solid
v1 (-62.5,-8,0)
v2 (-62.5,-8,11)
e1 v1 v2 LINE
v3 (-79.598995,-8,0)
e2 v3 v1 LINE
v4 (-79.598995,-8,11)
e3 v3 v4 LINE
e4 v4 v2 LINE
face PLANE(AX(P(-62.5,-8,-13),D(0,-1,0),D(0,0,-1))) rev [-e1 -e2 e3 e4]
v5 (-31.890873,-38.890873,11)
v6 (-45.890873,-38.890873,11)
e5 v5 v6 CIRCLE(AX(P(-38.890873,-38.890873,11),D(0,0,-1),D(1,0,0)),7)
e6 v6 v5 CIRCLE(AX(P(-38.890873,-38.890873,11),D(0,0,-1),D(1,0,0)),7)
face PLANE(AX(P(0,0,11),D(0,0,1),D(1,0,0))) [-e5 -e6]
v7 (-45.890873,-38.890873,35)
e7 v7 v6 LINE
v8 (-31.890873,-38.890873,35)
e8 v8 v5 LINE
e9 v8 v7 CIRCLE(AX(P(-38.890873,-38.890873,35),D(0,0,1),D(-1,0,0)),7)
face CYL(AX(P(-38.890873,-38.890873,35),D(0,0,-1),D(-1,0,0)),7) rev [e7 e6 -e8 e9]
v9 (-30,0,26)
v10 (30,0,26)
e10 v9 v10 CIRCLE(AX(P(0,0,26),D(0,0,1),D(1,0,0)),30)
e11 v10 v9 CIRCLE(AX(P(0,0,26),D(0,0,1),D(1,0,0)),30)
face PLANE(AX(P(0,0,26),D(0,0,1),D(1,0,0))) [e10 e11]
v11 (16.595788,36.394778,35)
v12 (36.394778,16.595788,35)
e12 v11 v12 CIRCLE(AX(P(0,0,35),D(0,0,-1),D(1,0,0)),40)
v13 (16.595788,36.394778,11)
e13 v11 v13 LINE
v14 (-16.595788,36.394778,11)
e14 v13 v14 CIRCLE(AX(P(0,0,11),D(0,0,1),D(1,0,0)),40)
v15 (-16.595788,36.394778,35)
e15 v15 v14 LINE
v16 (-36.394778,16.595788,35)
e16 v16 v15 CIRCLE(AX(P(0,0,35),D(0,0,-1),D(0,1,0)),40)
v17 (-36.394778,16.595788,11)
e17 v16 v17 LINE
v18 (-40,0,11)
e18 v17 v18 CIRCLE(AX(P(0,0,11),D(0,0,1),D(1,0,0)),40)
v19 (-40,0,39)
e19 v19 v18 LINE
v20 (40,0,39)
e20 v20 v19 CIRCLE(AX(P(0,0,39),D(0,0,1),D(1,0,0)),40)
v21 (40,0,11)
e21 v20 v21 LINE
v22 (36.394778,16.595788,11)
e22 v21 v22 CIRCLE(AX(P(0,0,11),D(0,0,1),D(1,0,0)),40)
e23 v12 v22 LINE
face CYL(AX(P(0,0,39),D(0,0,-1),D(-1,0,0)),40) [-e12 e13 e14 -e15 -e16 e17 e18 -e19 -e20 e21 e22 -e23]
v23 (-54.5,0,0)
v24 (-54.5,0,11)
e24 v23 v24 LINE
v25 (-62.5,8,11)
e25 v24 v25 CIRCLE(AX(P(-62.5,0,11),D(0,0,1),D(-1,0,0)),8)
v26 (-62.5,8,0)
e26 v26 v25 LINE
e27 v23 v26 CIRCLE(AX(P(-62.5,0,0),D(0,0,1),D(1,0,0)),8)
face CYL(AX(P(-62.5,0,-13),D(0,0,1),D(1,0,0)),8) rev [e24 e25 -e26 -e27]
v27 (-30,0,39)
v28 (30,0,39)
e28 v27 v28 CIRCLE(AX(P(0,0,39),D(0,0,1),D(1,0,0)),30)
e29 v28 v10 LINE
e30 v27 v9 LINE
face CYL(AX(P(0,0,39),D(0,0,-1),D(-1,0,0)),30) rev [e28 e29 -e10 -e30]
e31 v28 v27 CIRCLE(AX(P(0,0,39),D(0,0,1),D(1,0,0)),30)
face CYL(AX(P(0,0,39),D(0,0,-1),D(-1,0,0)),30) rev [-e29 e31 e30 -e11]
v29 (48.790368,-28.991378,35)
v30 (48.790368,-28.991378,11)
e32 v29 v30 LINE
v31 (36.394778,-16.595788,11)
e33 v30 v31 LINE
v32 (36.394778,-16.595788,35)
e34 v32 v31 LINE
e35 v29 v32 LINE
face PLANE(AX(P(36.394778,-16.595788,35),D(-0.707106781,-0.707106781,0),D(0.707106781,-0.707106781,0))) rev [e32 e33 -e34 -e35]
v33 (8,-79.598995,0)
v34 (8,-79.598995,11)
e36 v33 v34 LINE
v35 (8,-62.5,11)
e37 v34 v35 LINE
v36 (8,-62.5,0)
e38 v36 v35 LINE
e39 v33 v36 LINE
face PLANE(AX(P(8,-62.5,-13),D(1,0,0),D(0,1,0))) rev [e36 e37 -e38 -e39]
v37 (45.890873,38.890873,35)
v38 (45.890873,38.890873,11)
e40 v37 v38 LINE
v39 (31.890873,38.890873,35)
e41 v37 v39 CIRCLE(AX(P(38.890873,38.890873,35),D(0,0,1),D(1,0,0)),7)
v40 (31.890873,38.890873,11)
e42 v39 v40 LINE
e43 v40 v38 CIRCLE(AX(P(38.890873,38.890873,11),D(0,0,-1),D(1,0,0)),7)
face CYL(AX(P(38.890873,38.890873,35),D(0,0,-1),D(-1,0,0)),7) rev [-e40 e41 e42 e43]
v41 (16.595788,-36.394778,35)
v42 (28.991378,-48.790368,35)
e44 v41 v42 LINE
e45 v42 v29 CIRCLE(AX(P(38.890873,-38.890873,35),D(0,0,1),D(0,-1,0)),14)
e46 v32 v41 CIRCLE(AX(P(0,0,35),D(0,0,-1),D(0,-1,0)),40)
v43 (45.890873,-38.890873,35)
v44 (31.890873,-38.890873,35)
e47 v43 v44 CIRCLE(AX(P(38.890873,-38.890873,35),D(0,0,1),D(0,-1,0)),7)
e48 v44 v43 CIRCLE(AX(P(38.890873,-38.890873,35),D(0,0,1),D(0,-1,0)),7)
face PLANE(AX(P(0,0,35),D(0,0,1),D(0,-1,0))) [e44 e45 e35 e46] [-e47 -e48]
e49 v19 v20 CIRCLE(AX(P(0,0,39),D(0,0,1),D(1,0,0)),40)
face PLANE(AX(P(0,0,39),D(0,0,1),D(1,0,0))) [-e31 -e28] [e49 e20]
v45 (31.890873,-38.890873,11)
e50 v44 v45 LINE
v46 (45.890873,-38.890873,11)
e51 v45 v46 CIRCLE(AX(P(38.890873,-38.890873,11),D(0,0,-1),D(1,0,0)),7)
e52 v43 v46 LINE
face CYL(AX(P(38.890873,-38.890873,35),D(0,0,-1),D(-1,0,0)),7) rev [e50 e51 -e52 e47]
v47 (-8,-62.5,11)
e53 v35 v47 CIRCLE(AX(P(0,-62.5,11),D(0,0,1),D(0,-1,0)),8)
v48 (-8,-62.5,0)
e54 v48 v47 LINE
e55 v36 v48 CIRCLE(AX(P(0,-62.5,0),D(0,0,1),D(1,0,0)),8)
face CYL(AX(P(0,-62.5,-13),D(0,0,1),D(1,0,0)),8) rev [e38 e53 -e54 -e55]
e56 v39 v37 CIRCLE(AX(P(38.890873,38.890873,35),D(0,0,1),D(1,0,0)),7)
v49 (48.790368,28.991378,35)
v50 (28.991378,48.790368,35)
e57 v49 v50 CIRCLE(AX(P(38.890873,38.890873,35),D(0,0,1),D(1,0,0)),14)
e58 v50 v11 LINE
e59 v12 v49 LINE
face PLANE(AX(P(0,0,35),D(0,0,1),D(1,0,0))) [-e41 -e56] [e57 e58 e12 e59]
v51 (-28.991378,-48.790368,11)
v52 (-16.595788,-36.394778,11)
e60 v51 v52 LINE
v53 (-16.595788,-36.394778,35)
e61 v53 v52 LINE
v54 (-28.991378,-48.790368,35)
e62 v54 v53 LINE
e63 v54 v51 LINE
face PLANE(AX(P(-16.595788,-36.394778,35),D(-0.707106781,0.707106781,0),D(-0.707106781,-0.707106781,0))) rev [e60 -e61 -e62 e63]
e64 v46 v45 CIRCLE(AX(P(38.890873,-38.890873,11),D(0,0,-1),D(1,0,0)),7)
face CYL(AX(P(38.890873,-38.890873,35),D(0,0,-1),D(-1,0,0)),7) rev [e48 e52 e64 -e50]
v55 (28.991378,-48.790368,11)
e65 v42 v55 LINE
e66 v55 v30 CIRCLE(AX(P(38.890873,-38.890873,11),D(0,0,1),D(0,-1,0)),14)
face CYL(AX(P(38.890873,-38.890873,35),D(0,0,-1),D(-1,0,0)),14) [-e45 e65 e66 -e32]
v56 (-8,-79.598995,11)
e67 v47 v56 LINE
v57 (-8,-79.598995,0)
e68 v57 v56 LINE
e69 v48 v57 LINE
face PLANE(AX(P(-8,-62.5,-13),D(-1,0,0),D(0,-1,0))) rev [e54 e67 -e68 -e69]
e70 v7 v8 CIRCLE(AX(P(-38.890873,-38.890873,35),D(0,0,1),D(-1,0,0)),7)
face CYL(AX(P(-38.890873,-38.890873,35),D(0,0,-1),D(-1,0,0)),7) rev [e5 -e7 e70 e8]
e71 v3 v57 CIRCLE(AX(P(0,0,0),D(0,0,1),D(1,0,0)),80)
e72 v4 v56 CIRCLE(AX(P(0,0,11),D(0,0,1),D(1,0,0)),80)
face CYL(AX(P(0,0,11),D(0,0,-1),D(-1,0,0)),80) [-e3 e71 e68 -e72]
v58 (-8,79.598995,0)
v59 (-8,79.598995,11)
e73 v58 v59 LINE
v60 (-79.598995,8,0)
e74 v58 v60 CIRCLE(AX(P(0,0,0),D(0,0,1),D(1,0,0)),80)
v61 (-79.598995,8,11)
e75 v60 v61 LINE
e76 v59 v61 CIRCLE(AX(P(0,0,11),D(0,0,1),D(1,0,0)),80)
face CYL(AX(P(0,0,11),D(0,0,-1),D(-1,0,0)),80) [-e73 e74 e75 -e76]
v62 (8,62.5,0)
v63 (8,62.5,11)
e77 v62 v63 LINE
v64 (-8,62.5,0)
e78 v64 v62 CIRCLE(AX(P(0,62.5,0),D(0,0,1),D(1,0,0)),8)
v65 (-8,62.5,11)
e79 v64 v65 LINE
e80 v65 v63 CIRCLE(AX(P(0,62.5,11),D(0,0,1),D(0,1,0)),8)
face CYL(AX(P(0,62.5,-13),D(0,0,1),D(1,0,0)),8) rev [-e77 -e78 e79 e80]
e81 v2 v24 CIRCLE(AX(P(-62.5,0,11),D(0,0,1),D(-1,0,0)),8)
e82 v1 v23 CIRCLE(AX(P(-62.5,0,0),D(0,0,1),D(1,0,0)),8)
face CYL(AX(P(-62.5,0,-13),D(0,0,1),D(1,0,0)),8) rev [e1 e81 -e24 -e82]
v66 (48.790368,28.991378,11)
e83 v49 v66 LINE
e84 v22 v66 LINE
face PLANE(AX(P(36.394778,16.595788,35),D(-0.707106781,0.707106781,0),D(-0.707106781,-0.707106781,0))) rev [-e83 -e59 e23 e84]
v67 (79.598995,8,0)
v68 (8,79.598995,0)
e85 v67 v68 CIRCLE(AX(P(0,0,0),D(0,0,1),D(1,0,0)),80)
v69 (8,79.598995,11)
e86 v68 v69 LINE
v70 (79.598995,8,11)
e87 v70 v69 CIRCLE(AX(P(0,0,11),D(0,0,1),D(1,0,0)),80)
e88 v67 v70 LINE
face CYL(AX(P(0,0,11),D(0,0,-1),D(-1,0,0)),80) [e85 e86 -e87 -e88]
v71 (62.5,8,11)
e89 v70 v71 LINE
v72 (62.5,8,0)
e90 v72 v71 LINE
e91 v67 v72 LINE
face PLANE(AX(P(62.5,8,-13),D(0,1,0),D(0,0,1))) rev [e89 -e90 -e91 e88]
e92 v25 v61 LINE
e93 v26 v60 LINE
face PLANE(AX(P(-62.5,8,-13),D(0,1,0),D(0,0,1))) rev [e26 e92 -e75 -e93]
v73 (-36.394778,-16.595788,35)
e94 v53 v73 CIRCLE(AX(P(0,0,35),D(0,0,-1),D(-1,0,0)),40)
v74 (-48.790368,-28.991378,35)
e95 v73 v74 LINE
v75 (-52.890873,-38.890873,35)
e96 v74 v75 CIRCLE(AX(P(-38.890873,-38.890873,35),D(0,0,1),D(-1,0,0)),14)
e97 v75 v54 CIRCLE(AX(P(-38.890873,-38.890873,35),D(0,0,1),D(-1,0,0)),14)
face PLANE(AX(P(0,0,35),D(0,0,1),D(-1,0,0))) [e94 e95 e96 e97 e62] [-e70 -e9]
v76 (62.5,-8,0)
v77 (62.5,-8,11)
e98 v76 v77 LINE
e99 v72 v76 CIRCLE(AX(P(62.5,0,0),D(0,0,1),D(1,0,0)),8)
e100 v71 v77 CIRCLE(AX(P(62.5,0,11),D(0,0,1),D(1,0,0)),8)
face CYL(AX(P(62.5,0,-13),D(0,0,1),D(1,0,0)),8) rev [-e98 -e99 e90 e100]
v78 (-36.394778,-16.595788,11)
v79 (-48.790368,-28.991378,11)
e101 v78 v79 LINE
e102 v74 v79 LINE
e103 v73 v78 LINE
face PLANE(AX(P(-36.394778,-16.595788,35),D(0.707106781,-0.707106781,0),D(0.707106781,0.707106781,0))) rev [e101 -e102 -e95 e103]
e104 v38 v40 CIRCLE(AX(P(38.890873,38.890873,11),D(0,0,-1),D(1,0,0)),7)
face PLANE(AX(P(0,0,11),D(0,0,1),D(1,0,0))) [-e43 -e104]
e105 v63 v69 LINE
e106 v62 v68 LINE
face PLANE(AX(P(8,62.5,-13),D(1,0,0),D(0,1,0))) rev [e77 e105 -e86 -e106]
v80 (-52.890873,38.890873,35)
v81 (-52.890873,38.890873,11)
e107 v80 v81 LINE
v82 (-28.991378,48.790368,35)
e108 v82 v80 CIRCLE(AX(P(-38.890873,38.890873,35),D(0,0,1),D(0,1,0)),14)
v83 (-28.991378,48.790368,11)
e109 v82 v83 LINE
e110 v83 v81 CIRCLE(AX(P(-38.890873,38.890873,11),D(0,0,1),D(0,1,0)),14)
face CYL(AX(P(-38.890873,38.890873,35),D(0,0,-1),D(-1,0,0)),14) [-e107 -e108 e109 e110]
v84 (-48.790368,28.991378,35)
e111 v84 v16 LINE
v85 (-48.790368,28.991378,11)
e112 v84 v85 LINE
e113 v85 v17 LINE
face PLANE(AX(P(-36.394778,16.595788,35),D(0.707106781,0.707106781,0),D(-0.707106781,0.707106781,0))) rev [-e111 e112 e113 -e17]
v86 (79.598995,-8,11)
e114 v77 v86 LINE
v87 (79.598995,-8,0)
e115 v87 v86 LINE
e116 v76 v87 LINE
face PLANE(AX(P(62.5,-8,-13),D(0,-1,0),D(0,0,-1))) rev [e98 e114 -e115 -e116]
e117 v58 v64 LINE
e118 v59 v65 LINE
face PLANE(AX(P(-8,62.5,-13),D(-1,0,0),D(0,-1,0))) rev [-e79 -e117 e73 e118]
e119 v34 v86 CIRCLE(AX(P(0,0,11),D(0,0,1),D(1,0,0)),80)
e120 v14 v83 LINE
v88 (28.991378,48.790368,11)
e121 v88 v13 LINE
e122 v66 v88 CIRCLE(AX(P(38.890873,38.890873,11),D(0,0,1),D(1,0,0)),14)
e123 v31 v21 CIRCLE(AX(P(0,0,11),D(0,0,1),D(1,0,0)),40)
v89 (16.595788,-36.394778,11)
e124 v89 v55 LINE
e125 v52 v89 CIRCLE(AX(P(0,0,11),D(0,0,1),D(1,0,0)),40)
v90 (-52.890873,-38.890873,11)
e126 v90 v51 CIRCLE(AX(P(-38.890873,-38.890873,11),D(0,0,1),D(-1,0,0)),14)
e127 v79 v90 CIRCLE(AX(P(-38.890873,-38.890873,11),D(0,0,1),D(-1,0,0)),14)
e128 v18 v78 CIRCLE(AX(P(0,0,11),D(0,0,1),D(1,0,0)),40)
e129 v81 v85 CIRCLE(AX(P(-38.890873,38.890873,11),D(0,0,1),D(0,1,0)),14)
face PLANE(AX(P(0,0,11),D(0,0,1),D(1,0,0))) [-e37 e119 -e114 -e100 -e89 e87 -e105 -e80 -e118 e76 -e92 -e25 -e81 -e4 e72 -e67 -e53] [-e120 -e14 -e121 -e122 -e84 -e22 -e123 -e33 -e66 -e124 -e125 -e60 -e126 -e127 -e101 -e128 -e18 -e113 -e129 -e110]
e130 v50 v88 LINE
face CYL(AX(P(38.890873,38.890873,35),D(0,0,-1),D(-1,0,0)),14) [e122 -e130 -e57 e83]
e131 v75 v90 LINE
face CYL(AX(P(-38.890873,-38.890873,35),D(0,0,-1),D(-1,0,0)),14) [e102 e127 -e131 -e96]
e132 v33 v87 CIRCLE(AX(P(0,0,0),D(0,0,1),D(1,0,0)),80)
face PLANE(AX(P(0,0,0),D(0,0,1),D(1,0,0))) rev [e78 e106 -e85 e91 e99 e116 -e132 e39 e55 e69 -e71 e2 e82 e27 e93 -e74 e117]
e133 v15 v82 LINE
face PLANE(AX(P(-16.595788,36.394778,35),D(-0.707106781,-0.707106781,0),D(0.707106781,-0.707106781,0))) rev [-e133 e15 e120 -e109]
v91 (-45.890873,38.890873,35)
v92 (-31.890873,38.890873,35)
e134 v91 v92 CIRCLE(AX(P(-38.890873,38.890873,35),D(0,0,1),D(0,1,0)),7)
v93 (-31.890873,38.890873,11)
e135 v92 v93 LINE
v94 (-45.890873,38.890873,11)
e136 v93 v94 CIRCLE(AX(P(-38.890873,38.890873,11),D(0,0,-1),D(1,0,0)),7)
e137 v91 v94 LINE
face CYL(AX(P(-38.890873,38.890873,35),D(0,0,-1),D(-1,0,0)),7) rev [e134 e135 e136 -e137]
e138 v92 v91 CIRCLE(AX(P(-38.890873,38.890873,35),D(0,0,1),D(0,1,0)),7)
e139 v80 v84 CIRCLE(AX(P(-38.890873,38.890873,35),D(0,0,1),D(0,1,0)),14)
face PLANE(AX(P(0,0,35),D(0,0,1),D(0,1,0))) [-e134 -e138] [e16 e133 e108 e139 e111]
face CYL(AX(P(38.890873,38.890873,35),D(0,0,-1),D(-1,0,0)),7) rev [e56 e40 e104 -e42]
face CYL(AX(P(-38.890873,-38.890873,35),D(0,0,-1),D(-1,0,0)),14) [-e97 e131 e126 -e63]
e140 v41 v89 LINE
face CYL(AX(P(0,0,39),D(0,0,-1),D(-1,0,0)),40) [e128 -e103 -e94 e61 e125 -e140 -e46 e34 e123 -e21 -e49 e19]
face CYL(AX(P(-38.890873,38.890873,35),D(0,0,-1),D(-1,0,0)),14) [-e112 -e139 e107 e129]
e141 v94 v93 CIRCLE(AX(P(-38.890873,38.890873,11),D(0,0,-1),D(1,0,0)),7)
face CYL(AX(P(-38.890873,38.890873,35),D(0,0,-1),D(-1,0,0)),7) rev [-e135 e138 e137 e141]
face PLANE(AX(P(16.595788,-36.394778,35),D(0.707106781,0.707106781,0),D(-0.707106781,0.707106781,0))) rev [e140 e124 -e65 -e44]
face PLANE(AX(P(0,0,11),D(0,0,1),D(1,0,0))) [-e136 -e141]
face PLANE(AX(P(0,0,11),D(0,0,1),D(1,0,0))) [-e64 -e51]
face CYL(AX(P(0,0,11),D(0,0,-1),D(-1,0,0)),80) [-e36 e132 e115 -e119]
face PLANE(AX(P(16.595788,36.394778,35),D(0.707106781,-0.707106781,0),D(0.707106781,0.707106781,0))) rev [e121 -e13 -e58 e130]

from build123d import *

# Parameters (mm, degrees)
FLANGE_DISC_SKETCH_R          = 80
FLANGE_DISC_160_DEPTH         = 11
HUB_SKETCH_R                  = 40
HUB_SKETCH_R_2                = 30
HUB_80X_60_DEPTH              = 28
ROUND_BOSS_SKETCH_R           = 30
ROUND_BOSS_15MM_DEPTH         = 15
MOUNTING_LUG_SKETCH_R         = 7
MOUNTING_LUG_DEPTH            = 24
MOUNTING_LUG_PATTERN_4X_COUNT = 4
RIM_START                     = -24
RIM_SLOT_CUT_DEPTH            = 24
RIM_SLOT_PATTERN_4X_COUNT     = 4


with BuildPart() as part:
    # Flange Disc Sketch → Flange Disc Ø160 (new body)
    with BuildSketch(Plane.XY):
        Circle(FLANGE_DISC_SKETCH_R)
    extrude(amount=FLANGE_DISC_160_DEPTH)

    # Hub Sketch → Hub Ø80xØ60 (add)
    with BuildSketch(Plane.XY.offset(11)):
        Circle(HUB_SKETCH_R)
        Circle(HUB_SKETCH_R_2, mode=Mode.SUBTRACT)
    extrude(amount=HUB_80X_60_DEPTH)

    # Round Boss Sketch → Round Boss 15mm (add)
    with BuildSketch(Plane.XY.offset(11)):
        Circle(ROUND_BOSS_SKETCH_R)
    extrude(amount=ROUND_BOSS_15MM_DEPTH)

    # Mounting Lug Sketch → Mounting Lug (add)
    with BuildSketch(Plane.XY.offset(11)):
        with BuildLine():
            Line((16.595787662, 36.394777536), (28.991378029, 48.790367902))
            ThreePointArc((28.991378029, 48.790367902), (48.790367902, 48.790367902), (48.790367902, 28.991378029))
            Line((48.790367902, 28.991378029), (36.394777536, 16.595787662))
            ThreePointArc((36.394777536, 16.595787662), (28.284271247, 28.284271247), (16.595787662, 36.394777536))
        make_face()
        with Locations((38.890872965, 38.890872965)):
            Circle(MOUNTING_LUG_SKETCH_R, mode=Mode.SUBTRACT)
    mounting_lug = extrude(amount=MOUNTING_LUG_DEPTH)

    # Mounting Lug Pattern 4x: Mounting Lug ×4 about axis
    mounting_lug_pattern_4x_axis = Axis((0, 0, 0), (0, 0, 1))
    for i in range(1, MOUNTING_LUG_PATTERN_4X_COUNT):
        add(mounting_lug.rotate(mounting_lug_pattern_4x_axis, i * 360 / MOUNTING_LUG_PATTERN_4X_COUNT))

    # Rim Slot Sketch → Rim Slot Cut (cut)
    with BuildSketch(Plane.XY.offset(11).offset(RIM_START)):
        with BuildLine():
            Line((62.5, 8), (79.598994969, 8))
            ThreePointArc((79.598994969, 8), (80, 0), (79.598994969, -8))
            Line((79.598994969, -8), (62.5, -8))
            ThreePointArc((62.5, -8), (54.5, 0), (62.5, 8))
        make_face()
    rim_slot_cut = extrude(amount=RIM_SLOT_CUT_DEPTH, mode=Mode.SUBTRACT)

    # Rim Slot Pattern 4x: Rim Slot Cut ×4 about axis
    rim_slot_pattern_4x_axis = Axis((0, 0, 0), (0, 0, 1))
    for i in range(1, RIM_SLOT_PATTERN_4X_COUNT):
        add(rim_slot_cut.rotate(rim_slot_pattern_4x_axis, i * 360 / RIM_SLOT_PATTERN_4X_COUNT), mode=Mode.SUBTRACT)


solid = part.part
